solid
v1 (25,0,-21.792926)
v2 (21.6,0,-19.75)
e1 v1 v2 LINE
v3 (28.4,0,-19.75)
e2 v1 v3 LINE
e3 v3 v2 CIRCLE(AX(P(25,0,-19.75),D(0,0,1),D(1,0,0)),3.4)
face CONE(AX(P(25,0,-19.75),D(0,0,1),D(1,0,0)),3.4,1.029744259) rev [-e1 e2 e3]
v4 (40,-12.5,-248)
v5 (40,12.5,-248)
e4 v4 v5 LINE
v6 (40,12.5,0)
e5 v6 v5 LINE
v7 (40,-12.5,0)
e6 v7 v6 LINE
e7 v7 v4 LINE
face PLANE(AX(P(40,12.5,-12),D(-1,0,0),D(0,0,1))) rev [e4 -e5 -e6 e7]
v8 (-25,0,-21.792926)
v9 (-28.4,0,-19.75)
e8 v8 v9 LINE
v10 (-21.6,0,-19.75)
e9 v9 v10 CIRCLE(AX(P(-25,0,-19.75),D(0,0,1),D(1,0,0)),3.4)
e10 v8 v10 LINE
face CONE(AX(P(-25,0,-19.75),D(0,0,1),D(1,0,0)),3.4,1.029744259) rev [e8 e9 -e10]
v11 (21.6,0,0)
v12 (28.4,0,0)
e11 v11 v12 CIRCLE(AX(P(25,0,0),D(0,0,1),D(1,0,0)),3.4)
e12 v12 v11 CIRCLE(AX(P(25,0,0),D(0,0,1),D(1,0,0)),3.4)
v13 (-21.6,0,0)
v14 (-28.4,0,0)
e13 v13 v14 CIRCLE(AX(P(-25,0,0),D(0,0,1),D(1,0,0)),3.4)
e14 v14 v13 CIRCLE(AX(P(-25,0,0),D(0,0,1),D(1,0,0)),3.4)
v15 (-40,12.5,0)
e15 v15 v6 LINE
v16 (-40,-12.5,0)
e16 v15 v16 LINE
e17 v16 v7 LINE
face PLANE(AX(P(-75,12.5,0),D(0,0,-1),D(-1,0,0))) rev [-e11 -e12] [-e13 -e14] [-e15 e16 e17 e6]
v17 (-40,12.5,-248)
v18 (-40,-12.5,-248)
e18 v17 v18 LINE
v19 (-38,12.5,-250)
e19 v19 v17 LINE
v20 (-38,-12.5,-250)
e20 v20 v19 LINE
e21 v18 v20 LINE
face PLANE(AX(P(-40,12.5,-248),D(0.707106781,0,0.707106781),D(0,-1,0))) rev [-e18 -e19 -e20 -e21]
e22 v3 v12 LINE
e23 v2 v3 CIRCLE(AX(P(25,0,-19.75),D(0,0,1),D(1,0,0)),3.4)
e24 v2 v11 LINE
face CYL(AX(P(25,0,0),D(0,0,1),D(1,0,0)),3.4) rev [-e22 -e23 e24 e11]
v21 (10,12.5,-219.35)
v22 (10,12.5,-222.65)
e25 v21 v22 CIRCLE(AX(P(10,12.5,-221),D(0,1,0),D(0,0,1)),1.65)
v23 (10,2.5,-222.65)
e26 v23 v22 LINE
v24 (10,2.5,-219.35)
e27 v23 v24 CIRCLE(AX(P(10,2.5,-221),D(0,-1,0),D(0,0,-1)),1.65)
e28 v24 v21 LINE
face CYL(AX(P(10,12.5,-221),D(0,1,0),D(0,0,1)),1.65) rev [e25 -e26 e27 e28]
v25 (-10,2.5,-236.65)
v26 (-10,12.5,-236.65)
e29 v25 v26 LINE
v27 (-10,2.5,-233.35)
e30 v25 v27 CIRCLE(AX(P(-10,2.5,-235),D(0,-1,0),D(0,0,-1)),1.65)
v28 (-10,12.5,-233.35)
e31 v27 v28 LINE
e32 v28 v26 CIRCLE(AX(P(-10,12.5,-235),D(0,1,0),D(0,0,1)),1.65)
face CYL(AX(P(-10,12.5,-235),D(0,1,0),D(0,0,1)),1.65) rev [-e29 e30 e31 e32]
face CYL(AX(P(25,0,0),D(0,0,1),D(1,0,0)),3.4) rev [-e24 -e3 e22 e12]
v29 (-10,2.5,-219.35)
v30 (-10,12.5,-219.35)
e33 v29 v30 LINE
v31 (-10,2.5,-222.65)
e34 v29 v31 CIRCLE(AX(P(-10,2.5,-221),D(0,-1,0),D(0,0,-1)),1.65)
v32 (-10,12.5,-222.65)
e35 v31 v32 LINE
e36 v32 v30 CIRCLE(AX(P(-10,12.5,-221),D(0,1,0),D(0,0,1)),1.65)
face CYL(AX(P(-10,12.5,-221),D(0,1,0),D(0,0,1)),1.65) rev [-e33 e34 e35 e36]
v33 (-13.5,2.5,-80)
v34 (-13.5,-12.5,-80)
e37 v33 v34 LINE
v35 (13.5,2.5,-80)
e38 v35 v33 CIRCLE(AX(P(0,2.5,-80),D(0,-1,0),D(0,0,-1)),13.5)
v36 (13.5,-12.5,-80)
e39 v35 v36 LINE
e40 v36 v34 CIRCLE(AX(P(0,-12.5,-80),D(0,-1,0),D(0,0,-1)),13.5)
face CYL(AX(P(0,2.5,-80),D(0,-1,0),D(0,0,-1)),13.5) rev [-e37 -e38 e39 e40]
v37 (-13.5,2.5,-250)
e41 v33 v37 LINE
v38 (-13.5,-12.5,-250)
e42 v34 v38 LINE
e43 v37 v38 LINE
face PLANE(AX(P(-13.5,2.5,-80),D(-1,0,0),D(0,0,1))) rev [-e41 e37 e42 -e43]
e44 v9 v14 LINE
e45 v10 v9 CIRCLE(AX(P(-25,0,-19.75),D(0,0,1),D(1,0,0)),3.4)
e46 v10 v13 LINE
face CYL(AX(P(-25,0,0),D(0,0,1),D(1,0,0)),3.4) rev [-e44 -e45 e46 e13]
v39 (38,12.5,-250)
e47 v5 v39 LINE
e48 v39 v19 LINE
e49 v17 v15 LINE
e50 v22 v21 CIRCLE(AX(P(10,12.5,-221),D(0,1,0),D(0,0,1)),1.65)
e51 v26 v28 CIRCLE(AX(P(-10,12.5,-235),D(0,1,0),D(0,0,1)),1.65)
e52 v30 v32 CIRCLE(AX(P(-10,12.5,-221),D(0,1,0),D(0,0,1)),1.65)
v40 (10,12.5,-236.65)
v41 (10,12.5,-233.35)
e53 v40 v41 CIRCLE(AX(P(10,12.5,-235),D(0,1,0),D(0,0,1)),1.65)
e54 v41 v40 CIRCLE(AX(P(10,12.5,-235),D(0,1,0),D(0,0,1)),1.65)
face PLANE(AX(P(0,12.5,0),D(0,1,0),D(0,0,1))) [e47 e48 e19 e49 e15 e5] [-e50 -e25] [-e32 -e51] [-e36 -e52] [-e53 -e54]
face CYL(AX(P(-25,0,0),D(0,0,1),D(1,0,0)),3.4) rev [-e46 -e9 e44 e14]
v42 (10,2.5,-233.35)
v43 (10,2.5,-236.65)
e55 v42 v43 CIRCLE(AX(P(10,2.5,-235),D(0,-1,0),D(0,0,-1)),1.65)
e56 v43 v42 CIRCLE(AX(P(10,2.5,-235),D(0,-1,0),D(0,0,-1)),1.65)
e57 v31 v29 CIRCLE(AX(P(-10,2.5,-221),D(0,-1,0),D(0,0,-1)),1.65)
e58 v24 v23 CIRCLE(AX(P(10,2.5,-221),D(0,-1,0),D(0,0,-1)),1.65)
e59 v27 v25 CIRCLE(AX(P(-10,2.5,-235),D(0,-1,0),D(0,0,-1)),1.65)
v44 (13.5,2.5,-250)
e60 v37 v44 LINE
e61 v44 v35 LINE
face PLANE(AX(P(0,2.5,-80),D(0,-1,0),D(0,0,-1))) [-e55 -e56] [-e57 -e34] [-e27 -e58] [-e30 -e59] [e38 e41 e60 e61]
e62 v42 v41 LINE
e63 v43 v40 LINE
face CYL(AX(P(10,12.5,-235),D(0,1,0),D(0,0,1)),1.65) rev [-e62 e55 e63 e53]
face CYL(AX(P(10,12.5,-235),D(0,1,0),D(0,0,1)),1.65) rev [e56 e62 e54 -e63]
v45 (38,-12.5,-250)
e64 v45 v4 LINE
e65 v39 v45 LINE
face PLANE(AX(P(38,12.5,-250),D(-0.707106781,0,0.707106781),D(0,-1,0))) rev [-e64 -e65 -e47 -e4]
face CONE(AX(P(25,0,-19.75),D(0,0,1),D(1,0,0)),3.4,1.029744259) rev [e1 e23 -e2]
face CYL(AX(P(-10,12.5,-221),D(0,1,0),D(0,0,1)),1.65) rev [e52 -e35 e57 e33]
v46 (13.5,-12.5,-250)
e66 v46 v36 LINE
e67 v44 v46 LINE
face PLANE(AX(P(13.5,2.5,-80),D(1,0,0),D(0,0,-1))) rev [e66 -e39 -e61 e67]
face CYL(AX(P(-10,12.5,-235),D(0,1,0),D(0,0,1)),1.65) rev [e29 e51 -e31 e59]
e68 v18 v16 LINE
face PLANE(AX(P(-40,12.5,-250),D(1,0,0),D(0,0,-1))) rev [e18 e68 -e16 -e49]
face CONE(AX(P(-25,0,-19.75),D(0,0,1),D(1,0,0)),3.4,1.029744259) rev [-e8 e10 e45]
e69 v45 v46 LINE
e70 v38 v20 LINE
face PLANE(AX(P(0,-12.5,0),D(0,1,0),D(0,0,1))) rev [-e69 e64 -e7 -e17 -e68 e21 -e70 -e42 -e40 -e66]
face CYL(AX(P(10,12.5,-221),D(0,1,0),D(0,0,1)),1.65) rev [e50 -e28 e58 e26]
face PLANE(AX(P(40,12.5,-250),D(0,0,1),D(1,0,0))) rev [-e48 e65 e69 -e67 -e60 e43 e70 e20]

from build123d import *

# Parameters (mm, degrees)
BOSS_EXTRUDE1_DEPTH   = 12.5
CHAMFER1_SIZE         = 2
HOLE1_D               = 9
CUT_EXTRUDE1_DEPTH    = 15
M4_TAPPED_HOLE1_D     = 3.3
SKETCH11_W            = 35
SKETCH11_H            = 25
CUT_EXTRUDE2_DEPTH    = 250.850455273
M8_TAPPED_HOLE2_D     = 6.8
M8_TAPPED_HOLE2_DEPTH = 19.75
M8_TAPPED_HOLE2_TIP   = 2.042926105


with BuildPart() as part:
    # Sketch1 → Boss-Extrude1 (new, symmetric)
    with BuildSketch(Plane(origin=(0, 0, 0), x_dir=(1, 0, 0), z_dir=(0, 1, 0))):
        Polygon((-75, 0), (75, 0), (75, 12), (40, 12), (40, 250), (-40, 250), (-40, 12), (-75, 12), align=None)
    extrude(amount=BOSS_EXTRUDE1_DEPTH, both=True)

    # Chamfer1
    chamfer1_edges = [part.edges().sort_by_distance(p)[0] for p in [
        (-75, 0, -12),
        (-40, 0, -250),
        (40, 0, -250),
        (75, 0, -12),
    ]]
    chamfer(chamfer1_edges, length=CHAMFER1_SIZE)

    # Hole1 (through all)
    with Locations(Plane.XY):
        with Locations((-60, 0), (60, 0)):
            Hole(HOLE1_D / 2)

    # Sketch4 → Cut-Extrude1 (cut)
    with BuildSketch(Plane(origin=(0, -12.5, 0), x_dir=(-1, 0, 0), z_dir=(0, -1, 0))):
        with BuildLine():
            Line((-13.5, 80), (-13.5, 250))
            ThreePointArc((-13.5, 250), (0, 263.5), (13.5, 250))
            Line((13.5, 250), (13.5, 80))
            ThreePointArc((13.5, 80), (0, 66.5), (-13.5, 80))
        make_face()
    extrude(amount=-CUT_EXTRUDE1_DEPTH, mode=Mode.SUBTRACT)

    # M4 Tapped Hole1 (through all)
    with Locations(Plane(origin=(0, 12.5, 0), x_dir=(1, 0, 0), z_dir=(0, 1, 0))):
        with Locations((-10, 235), (-10, 221), (10, 221), (10, 235)):
            Hole(M4_TAPPED_HOLE1_D / 2)

    # Sketch11 → Cut-Extrude2 (cut, through all)
    with BuildSketch(Plane(origin=(0, 0, -12), x_dir=(-1, 0, 0), z_dir=(0, 0, -1))):
        with Locations((-57.5, 0)):
            Rectangle(SKETCH11_W, SKETCH11_H)
        with Locations((57.5, 0)):
            Rectangle(SKETCH11_W, SKETCH11_H)
    extrude(amount=-CUT_EXTRUDE2_DEPTH, mode=Mode.SUBTRACT)

    # M8 Tapped Hole2
    with Locations(Plane.XY):
        with Locations((-25, 0), (25, 0)):
            Hole(M8_TAPPED_HOLE2_D / 2, depth=M8_TAPPED_HOLE2_DEPTH)
            with Locations((0, 0, -(M8_TAPPED_HOLE2_DEPTH + M8_TAPPED_HOLE2_TIP / 2))):  # 118° drill point
                Cone(0, M8_TAPPED_HOLE2_D / 2, M8_TAPPED_HOLE2_TIP, mode=Mode.SUBTRACT)


solid = part.part
